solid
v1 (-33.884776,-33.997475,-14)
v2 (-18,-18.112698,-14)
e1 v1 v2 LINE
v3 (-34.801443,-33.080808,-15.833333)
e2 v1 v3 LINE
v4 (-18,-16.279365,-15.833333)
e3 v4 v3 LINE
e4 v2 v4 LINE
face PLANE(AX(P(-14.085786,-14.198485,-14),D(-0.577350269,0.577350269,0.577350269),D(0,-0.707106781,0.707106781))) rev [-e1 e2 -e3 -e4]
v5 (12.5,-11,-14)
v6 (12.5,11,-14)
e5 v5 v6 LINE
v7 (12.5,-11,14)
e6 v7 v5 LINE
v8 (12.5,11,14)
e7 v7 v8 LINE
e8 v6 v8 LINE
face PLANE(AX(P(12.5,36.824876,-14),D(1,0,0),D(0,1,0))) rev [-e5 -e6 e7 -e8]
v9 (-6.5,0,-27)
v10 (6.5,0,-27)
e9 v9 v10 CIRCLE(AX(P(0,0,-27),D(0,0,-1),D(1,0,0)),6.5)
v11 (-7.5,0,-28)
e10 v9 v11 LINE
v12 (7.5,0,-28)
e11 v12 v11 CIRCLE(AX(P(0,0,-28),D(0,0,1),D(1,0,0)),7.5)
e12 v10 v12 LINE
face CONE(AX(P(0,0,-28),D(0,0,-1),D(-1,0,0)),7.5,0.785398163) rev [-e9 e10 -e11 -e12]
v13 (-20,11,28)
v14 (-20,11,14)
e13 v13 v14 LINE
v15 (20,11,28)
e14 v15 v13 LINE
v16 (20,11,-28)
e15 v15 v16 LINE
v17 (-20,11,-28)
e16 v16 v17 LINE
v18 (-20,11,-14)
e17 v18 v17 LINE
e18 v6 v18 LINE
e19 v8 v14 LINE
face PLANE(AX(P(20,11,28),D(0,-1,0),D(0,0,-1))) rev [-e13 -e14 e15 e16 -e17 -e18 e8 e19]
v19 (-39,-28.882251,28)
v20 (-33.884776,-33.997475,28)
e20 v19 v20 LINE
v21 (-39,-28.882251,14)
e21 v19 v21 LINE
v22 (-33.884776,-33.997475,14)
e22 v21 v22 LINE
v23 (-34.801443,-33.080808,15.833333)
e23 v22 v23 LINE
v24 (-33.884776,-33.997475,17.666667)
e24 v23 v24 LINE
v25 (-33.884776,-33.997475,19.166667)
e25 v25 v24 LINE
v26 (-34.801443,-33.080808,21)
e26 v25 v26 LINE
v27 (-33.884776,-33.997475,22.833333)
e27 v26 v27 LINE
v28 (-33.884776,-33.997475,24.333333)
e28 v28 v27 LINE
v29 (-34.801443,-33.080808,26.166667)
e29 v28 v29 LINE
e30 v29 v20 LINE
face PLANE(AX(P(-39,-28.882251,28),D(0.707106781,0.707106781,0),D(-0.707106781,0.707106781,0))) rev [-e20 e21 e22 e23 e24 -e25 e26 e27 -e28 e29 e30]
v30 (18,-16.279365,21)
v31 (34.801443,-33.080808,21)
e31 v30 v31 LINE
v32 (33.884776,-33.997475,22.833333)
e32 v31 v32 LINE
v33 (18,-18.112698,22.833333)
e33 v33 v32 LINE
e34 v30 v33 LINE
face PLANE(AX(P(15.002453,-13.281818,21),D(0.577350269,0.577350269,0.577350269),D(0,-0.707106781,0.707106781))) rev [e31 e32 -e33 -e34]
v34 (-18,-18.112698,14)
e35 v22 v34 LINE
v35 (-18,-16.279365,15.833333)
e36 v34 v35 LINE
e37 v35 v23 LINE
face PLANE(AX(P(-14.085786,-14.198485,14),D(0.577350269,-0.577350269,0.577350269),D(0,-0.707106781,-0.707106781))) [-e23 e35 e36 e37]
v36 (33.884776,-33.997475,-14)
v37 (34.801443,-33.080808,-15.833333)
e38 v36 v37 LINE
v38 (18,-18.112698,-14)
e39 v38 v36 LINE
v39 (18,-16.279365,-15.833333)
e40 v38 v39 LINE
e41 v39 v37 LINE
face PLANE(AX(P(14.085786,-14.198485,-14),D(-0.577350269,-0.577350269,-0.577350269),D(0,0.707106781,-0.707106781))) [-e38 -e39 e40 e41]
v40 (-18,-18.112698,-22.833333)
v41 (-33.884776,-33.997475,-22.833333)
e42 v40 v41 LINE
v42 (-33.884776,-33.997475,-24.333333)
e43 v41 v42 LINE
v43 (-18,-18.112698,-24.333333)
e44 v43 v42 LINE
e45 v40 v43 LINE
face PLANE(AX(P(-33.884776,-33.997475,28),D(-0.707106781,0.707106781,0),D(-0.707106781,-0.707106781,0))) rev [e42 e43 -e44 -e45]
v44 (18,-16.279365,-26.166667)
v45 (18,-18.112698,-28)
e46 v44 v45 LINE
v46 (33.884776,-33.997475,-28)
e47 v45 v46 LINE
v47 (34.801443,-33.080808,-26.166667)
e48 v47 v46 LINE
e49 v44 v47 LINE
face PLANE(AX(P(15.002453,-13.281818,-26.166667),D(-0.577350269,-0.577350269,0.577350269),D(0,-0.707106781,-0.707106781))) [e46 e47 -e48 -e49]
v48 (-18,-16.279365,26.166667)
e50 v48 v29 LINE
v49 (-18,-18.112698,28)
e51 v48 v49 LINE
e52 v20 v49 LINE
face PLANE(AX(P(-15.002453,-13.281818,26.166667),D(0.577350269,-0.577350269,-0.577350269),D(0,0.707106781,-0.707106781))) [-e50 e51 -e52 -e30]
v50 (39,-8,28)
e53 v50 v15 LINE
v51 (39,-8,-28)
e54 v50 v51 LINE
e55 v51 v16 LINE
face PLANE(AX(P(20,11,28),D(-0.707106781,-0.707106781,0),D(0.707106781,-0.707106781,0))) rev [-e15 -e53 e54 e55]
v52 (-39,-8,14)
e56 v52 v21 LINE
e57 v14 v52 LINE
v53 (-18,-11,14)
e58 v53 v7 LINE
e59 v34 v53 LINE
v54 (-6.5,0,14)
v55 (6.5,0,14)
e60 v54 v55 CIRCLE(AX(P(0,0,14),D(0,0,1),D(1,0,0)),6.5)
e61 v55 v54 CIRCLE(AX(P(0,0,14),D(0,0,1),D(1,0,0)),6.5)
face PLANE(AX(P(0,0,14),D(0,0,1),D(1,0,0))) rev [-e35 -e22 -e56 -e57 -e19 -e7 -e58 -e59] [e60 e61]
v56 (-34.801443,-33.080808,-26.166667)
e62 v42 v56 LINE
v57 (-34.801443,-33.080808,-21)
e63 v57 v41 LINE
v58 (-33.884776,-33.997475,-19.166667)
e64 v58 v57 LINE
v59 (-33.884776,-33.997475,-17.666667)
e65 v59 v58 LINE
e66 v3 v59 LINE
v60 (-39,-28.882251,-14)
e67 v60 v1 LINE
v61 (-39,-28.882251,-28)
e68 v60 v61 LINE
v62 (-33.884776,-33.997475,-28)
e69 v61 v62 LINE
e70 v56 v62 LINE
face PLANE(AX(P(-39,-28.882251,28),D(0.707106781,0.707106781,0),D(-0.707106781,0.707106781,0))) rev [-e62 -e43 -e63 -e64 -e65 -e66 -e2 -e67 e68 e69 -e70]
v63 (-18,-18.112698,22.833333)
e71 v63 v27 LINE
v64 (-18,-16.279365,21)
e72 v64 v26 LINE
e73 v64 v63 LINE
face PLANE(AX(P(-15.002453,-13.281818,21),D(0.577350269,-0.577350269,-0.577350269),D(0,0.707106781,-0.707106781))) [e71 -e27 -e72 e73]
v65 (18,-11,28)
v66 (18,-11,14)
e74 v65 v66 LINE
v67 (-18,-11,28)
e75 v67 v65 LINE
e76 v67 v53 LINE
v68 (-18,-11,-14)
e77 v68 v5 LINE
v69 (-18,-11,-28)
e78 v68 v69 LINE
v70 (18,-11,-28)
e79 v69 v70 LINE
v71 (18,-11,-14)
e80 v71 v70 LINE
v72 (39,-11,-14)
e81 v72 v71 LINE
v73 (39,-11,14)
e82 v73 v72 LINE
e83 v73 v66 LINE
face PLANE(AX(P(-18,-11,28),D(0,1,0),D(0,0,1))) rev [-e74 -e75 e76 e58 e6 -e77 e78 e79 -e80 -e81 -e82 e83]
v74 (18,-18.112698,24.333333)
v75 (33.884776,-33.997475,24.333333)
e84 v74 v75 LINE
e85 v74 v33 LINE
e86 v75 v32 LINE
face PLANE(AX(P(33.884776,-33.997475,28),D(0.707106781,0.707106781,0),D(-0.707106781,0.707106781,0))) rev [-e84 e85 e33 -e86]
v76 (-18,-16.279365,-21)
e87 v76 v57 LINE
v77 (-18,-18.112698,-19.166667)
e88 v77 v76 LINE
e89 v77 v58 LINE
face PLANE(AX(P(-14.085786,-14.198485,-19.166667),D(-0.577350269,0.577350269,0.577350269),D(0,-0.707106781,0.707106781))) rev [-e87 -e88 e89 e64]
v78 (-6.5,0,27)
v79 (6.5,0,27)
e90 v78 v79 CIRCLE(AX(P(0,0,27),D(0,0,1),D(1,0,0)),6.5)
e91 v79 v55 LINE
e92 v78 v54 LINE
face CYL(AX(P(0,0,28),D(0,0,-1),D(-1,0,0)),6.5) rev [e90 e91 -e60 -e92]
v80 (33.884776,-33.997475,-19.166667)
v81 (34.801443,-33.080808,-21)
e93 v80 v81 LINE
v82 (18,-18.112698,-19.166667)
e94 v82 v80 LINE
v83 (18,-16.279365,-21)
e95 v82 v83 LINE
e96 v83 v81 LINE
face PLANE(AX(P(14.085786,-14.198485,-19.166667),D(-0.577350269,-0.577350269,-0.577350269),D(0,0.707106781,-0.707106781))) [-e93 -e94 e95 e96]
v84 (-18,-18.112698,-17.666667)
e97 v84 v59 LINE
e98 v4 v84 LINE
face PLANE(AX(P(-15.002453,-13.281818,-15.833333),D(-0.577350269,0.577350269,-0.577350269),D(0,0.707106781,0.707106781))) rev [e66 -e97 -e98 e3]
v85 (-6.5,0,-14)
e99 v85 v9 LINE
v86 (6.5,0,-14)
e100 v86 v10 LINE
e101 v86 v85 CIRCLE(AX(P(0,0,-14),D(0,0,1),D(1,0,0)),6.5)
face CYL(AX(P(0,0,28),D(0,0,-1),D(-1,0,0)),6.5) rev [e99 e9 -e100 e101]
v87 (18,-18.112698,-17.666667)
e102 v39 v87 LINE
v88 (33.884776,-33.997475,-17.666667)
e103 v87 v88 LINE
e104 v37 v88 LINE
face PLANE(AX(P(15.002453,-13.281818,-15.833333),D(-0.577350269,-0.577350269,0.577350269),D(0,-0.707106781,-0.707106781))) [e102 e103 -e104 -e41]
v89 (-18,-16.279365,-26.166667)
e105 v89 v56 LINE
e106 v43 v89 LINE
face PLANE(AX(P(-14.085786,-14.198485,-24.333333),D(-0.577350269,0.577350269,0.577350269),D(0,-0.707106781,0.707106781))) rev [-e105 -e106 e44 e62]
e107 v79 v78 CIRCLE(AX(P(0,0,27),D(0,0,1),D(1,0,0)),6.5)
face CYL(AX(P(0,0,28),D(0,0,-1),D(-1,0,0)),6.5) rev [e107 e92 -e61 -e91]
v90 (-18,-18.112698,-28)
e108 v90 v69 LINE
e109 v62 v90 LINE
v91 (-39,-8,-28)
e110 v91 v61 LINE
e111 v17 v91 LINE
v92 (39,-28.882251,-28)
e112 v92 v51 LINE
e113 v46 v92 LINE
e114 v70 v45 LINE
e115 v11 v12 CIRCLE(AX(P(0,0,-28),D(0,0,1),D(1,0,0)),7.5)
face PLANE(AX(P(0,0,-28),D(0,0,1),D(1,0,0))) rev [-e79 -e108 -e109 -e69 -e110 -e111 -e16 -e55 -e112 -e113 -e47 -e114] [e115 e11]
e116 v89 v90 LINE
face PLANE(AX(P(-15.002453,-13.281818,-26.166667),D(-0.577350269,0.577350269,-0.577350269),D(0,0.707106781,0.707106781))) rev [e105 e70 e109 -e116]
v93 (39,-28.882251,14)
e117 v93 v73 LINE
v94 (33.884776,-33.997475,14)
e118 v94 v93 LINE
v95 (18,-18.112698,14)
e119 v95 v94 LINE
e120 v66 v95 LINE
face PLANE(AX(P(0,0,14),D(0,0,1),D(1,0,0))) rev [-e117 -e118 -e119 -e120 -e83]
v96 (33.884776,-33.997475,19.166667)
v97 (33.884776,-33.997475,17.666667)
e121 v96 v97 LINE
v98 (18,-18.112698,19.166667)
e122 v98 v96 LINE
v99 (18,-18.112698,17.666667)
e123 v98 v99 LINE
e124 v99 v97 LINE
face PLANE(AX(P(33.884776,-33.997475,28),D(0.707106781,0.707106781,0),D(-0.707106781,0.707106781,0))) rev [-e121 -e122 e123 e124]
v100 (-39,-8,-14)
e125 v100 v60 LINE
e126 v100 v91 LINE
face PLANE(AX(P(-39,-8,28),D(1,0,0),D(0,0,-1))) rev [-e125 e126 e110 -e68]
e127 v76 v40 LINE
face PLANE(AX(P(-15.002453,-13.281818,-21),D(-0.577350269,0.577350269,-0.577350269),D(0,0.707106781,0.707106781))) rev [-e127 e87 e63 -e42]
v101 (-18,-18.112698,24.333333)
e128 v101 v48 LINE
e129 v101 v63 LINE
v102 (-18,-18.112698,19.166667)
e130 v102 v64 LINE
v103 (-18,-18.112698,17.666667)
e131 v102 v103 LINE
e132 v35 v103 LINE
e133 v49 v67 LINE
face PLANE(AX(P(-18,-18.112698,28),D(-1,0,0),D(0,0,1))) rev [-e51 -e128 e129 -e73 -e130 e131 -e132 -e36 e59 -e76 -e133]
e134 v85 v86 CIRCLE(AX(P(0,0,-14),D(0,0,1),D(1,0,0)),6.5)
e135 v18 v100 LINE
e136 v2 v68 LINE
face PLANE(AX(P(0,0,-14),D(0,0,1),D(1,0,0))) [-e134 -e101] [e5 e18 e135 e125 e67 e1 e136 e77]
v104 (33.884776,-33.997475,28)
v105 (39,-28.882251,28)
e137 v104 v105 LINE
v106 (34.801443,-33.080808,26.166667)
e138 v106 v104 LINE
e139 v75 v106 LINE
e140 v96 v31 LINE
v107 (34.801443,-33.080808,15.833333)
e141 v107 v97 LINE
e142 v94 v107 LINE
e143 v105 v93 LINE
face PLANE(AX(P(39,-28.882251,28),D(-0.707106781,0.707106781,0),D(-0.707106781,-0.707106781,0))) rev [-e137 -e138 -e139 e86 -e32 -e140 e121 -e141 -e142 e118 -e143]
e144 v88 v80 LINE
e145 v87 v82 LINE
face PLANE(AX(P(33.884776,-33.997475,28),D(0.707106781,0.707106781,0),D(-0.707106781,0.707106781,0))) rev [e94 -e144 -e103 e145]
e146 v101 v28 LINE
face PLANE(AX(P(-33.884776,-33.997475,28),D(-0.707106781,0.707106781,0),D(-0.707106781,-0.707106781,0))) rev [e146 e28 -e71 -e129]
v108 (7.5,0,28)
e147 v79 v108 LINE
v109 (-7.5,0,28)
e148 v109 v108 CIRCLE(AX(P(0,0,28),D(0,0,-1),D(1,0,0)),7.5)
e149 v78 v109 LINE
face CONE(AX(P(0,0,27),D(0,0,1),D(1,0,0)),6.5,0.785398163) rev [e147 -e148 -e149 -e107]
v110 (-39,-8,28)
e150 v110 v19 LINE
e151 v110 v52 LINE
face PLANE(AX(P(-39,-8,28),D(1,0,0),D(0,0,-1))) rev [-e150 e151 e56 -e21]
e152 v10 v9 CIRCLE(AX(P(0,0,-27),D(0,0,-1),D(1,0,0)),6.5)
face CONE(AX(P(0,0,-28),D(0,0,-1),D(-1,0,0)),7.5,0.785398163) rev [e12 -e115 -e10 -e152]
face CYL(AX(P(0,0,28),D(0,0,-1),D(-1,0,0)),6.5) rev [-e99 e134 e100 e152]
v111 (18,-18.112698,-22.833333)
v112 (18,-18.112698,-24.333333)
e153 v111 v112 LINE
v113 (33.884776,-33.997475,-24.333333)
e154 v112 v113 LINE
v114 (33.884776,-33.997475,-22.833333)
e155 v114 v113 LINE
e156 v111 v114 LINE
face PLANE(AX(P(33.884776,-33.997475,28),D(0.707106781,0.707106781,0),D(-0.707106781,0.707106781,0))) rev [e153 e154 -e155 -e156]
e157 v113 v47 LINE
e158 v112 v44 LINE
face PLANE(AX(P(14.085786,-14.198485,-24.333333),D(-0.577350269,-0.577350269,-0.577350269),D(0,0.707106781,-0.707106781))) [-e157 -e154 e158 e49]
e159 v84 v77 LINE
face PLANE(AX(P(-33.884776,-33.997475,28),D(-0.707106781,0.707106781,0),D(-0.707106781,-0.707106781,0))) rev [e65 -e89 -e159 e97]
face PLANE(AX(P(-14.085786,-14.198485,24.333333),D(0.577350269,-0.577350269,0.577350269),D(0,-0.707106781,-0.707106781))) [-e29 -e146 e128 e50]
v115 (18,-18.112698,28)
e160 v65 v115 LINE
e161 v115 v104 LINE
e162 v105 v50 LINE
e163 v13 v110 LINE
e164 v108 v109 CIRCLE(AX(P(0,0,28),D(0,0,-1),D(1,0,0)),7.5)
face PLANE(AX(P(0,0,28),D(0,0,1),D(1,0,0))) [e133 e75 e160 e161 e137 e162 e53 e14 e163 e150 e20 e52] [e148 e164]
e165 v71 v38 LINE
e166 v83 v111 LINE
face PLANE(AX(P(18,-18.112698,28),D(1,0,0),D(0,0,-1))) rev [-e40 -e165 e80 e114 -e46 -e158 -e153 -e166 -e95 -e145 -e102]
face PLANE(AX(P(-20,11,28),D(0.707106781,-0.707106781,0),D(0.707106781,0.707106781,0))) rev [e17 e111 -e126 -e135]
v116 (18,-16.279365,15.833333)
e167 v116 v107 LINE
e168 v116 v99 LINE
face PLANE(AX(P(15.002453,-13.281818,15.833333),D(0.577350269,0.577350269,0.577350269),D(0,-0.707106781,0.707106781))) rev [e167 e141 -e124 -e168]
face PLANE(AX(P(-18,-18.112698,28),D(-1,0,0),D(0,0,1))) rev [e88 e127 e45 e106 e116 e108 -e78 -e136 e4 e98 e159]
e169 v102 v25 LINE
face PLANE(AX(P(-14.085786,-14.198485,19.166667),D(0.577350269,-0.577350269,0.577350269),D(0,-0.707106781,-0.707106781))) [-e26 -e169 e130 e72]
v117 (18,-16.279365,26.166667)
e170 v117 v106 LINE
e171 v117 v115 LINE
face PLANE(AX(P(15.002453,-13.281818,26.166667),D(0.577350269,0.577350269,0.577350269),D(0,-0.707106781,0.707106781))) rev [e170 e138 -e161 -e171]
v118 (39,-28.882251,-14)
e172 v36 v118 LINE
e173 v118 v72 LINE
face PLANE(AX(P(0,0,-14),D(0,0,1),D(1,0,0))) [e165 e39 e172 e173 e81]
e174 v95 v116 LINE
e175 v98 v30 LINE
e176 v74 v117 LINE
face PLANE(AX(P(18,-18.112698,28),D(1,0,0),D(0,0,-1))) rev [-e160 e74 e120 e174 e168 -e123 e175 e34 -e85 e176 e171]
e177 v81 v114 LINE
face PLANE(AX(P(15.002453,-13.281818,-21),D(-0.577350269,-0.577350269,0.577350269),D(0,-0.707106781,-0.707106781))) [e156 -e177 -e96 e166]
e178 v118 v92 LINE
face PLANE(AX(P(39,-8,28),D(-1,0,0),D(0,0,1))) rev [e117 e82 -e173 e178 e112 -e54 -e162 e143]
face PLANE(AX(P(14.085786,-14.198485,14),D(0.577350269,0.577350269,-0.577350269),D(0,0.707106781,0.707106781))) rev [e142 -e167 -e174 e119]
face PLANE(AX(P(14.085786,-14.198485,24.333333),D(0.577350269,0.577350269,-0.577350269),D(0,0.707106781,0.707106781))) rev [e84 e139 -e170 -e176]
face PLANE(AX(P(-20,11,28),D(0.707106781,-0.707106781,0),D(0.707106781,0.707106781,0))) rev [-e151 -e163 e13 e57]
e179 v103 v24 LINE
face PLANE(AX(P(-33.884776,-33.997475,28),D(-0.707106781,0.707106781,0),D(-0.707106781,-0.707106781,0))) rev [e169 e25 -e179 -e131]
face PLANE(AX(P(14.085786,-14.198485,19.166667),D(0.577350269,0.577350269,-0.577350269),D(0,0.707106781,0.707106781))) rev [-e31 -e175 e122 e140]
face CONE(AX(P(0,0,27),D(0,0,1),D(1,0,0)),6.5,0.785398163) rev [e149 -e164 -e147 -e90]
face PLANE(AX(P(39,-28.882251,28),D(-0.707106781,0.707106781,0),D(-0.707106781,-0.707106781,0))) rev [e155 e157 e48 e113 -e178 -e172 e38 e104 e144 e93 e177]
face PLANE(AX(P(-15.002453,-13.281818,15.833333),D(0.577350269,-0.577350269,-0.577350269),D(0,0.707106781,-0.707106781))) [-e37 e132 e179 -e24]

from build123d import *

# Parameters (mm, degrees)
SKETCH1_R            = 6.5
BOSS_EXTRUDE1_DEPTH  = 28
CUT_EXTRUDE1_START   = -14
SKETCH2_W            = 65.403152184
SKETCH2_H            = 73.649752858
CUT_EXTRUDE1_DEPTH   = 28
CUT_EXTRUDE2_DEPTH   = 28
MIRROR2_COPY_1_DEPTH = 28
CHAMFER1_SIZE        = 1
CUT_EXTRUDE3_START   = -14
SKETCH6_W            = 28.147073634
SKETCH6_H            = 26.396452471
CUT_EXTRUDE3_DEPTH   = 28


with BuildPart() as part:
    # Sketch1 → Boss-Extrude1 (new, symmetric)
    with BuildSketch(Plane.XY):
        Polygon((20, 11), (-20, 11), (-39, -8), (-39, -28.882250994), (-33.884776311, -33.997474683), (-18, -18.112698372), (-18, -11), (18, -11), (18, -18.112698372), (33.884776311, -33.997474683), (39, -28.882250994), (39, -8), align=None)
        Circle(SKETCH1_R, mode=Mode.SUBTRACT)
    extrude(amount=BOSS_EXTRUDE1_DEPTH, both=True)

    # Sketch2 → Cut-Extrude1 (cut)
    with BuildSketch(Plane.XY.offset(28).offset(CUT_EXTRUDE1_START)):
        with Locations((-20.201576092, 0)):
            Rectangle(SKETCH2_W, SKETCH2_H)
    extrude(amount=-CUT_EXTRUDE1_DEPTH, mode=Mode.SUBTRACT)

    # Sketch5 → Cut-Extrude2 (cut)
    with BuildSketch(Plane(origin=(-33.941125497, -33.941125497, 0), x_dir=(0, 0, 1), z_dir=(-0.7071067811865506, -0.7071067811865445, 0))):
        Polygon((-22.833333333, -0.079689783), (-19.166666667, -0.079689783), (-21, 1.216672649), align=None)
        Polygon((-17.666666667, -0.079689783), (-14, -0.079689783), (-15.833333333, 1.216672649), align=None)
        Polygon((-24.333333333, -0.079689783), (-26.166666667, 1.216672649), (-28, -0.079689783), align=None)
    cut_extrude2 = extrude(amount=-CUT_EXTRUDE2_DEPTH, mode=Mode.SUBTRACT)

    # Mirror1: Cut-Extrude2 across plane
    add(cut_extrude2.mirror(Plane.XY), mode=Mode.SUBTRACT)

    # Mirror2: Cut-Extrude2 across plane
    add(cut_extrude2.mirror(Plane(origin=(0, 0, 0), x_dir=(0, 0, 1), z_dir=(1, 0, 0))), mode=Mode.SUBTRACT)

    # Mirror2 copy 1 sketch → Mirror2 copy 1 (cut)
    with BuildSketch(Plane(origin=(33.941125497, -33.941125497, 0), x_dir=(0, 0, -1), z_dir=(0.7071067811865506, -0.7071067811865445, 0))):
        Polygon((-22.833333333, -0.079689783), (-19.166666667, -0.079689783), (-21, 1.216672649), align=None)
        Polygon((-17.666666667, -0.079689783), (-14, -0.079689783), (-15.833333333, 1.216672649), align=None)
        Polygon((-24.333333333, -0.079689783), (-26.166666667, 1.216672649), (-28, -0.079689783), align=None)
    extrude(amount=-MIRROR2_COPY_1_DEPTH, mode=Mode.SUBTRACT)

    # Chamfer1
    chamfer1_edges = [part.edges().sort_by_distance(p)[0] for p in [
        (-6.5, 0, -28),
        (-6.5, 0, 28),
    ]]
    chamfer(chamfer1_edges, length=CHAMFER1_SIZE)

    # Sketch6 → Cut-Extrude3 (cut)
    with BuildSketch(Plane.XY.offset(28).offset(CUT_EXTRUDE3_START)):
        with Locations((32.073536817, -24.198226236)):
            Rectangle(SKETCH6_W, SKETCH6_H)
    extrude(amount=-CUT_EXTRUDE3_DEPTH, mode=Mode.SUBTRACT)


solid = part.part
